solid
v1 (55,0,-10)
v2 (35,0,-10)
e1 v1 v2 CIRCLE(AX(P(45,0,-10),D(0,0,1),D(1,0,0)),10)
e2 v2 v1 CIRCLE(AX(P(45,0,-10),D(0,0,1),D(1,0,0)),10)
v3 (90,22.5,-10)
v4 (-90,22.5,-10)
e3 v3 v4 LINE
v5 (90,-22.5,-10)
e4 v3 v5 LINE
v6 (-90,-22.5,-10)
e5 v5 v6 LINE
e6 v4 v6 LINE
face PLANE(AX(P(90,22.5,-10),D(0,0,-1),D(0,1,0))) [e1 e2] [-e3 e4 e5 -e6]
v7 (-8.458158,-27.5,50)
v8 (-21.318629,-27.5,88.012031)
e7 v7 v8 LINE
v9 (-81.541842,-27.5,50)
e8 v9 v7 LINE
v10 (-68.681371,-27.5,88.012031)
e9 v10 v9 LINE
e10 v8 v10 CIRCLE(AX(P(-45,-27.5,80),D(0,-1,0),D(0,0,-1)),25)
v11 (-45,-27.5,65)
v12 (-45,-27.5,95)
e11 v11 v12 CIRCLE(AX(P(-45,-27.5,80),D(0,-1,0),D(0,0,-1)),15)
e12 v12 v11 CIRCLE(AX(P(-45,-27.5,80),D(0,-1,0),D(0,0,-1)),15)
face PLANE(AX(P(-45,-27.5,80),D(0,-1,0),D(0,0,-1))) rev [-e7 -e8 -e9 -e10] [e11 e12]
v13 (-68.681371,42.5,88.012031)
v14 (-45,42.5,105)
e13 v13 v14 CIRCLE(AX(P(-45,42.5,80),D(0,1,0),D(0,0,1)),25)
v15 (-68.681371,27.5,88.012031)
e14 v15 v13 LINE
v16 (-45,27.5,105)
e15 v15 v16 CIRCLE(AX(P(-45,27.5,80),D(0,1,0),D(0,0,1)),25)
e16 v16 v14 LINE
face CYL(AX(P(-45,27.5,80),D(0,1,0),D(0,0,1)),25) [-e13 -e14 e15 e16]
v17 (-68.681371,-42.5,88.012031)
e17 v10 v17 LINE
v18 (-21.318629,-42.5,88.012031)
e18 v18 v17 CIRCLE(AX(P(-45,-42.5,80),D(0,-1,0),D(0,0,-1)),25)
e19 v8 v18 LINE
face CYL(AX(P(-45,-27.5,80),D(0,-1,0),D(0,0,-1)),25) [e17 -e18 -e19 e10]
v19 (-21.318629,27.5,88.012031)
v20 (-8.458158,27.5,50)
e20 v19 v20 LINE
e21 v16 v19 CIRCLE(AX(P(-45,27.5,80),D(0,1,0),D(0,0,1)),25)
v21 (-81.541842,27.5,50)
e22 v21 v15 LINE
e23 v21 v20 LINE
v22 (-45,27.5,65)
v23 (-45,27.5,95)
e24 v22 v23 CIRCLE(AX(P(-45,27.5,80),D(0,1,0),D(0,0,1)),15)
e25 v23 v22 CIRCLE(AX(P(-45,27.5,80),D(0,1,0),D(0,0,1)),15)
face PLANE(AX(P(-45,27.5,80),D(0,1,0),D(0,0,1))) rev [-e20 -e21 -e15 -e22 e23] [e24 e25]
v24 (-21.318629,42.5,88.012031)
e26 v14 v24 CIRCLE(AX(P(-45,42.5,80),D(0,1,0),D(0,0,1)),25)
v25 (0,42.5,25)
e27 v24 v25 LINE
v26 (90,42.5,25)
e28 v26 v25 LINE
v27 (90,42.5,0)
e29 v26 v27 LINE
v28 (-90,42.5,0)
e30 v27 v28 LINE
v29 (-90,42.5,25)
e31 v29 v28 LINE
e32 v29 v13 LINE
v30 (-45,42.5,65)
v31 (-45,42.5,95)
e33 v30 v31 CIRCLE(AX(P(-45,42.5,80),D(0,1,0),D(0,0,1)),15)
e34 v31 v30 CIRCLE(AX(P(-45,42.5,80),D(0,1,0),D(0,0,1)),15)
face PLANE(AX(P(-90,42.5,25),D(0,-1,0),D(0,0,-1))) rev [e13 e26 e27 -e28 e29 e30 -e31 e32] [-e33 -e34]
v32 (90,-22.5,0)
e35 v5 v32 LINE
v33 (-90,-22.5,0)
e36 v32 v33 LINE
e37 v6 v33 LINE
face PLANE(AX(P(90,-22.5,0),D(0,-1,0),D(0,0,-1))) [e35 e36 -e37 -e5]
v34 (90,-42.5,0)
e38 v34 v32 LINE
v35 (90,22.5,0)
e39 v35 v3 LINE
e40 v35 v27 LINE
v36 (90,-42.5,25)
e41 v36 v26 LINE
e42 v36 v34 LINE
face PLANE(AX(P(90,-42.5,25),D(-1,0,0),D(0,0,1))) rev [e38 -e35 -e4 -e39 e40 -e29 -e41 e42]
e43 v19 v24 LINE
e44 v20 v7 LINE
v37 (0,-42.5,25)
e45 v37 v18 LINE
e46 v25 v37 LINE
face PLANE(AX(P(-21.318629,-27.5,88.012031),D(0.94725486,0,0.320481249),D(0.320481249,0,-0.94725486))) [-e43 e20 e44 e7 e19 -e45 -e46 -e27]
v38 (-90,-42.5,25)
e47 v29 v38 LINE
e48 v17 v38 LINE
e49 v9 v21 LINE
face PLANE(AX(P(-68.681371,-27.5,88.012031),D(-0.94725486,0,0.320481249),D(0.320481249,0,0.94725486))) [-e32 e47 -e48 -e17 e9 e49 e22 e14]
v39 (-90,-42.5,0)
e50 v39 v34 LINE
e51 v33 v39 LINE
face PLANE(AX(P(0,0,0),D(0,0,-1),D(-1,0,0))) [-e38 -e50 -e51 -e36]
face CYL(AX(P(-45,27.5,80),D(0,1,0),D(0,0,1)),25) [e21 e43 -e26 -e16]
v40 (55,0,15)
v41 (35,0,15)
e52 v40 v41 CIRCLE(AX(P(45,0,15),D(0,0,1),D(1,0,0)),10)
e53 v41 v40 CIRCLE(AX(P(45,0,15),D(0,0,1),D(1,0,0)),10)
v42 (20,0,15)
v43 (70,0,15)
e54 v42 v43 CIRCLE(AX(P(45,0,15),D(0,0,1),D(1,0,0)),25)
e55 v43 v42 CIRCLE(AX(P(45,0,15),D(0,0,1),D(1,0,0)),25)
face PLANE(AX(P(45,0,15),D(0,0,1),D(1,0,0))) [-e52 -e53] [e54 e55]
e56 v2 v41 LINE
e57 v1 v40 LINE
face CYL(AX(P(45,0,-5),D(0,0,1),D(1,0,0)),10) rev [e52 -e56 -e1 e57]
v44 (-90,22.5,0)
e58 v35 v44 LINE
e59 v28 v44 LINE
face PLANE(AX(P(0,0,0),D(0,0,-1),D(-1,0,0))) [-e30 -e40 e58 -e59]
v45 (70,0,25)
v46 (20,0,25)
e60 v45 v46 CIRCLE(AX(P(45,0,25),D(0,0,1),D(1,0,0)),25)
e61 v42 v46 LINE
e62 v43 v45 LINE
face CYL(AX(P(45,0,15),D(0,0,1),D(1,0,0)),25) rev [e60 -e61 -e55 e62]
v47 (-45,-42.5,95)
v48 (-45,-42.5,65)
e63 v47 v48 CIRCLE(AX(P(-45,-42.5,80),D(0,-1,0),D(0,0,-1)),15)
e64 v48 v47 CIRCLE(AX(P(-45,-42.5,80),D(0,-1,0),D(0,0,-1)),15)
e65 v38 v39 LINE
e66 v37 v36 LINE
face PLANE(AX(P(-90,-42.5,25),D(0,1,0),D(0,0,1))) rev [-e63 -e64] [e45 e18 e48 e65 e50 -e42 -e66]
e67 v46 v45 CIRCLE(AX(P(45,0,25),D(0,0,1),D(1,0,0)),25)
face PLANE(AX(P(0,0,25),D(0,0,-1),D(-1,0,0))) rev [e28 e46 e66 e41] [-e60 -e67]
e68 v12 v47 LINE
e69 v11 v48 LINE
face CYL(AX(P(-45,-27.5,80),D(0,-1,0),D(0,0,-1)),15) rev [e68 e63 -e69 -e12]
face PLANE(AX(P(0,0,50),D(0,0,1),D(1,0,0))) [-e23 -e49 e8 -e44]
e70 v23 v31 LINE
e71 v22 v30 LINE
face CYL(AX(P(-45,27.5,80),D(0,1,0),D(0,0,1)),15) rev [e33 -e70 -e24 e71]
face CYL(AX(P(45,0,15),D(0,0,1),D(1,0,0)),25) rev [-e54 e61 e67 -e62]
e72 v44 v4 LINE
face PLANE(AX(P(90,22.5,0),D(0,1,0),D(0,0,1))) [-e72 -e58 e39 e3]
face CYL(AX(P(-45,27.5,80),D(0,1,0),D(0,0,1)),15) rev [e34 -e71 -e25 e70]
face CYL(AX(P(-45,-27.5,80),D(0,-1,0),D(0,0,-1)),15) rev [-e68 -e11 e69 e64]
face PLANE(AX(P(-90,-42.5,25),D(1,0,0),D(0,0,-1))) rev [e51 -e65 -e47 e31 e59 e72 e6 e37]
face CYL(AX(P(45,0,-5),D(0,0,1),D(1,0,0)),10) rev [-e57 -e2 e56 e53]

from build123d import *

# Parameters (mm, degrees)
BASE_PLATE_SKETCH_W   = 180
BASE_PLATE_SKETCH_H   = 85
BASE_PLATE_DEPTH      = 25
COUNTERBORE_SKETCH_R  = 25
COUNTERBORE_50_DEPTH  = 10
THROUGH_HOLE_SKETCH_R = 10
THROUGH_HOLE_20_DEPTH = 20
BACK_KEY_SKETCH_W     = 10
BACK_KEY_SKETCH_H     = 45
BACK_KEY_DEPTH        = 180
KEY_RELIEF_SKETCH_R   = 10
KEY_RELIEF_CUT_DEPTH  = 103.621878759
UPPER_LUG_SKETCH_R    = 15
UPPER_LUG_DEPTH       = 15
LOWER_START           = -15
LOWER_LUG_SKETCH_R    = 15
LOWER_LUG_DEPTH       = 15
LUG_WEB_SKETCH_W      = 90
LUG_WEB_SKETCH_H      = 55
LUG_WEB_DEPTH         = 25
WEB_CUT_A_DEPTH       = 156
WEB_CUT_B_DEPTH       = 156


with BuildPart() as part:
    # Base Plate Sketch → Base Plate (new body)
    with BuildSketch(Plane.XY):
        Rectangle(BASE_PLATE_SKETCH_W, BASE_PLATE_SKETCH_H)
    extrude(amount=BASE_PLATE_DEPTH)

    # Counterbore Sketch → Counterbore Ø50 (cut)
    with BuildSketch(Plane.XY.offset(25)):
        with Locations((45, 0)):
            Circle(COUNTERBORE_SKETCH_R)
    extrude(amount=-COUNTERBORE_50_DEPTH, mode=Mode.SUBTRACT)

    # Through Hole Sketch → Through Hole Ø20 (cut)
    with BuildSketch(Plane.XY.offset(15)):
        with Locations((45, 0)):
            Circle(THROUGH_HOLE_SKETCH_R)
    extrude(amount=-THROUGH_HOLE_20_DEPTH, mode=Mode.SUBTRACT)

    # Back Key Sketch → Back Key (add, through all)
    with BuildSketch(Plane.ZY.offset(90)):
        with Locations((-5, 0)):
            Rectangle(BACK_KEY_SKETCH_W, BACK_KEY_SKETCH_H)
    extrude(amount=-BACK_KEY_DEPTH)

    # Key Relief Sketch → Key Relief Cut (cut, through all)
    with BuildSketch(Plane.XY):
        with Locations((45, 0)):
            Circle(KEY_RELIEF_SKETCH_R)
    extrude(amount=-KEY_RELIEF_CUT_DEPTH, mode=Mode.SUBTRACT)

    # Upper Lug Sketch → Upper Lug (add)
    with BuildSketch(Plane.XZ.offset(42.5)):
        with BuildLine():
            Line((-68.681371492, 88.01203122), (-90, 25))
            Line((-90, 25), (0, 25))
            Line((0, 25), (-21.318628508, 88.01203122))
            ThreePointArc((-21.318628508, 88.01203122), (-45, 105), (-68.681371492, 88.01203122))
        make_face()
        with Locations(Location((-45, 80, 0), (0, 0, 270))):
            Circle(UPPER_LUG_SKETCH_R, mode=Mode.SUBTRACT)
    extrude(amount=-UPPER_LUG_DEPTH)

    # Lower Lug Sketch → Lower Lug (add)
    with BuildSketch(Plane(origin=(0, 42.5, 0), x_dir=(1, 0, 0), z_dir=(0, 1, 0)).offset(LOWER_START)):
        with BuildLine():
            Line((-90, -25), (-68.681371492, -88.01203122))
            ThreePointArc((-68.681371492, -88.01203122), (-45, -105), (-21.318628508, -88.01203122))
            Line((-21.318628508, -88.01203122), (0, -25))
            Line((0, -25), (-90, -25))
        make_face()
        with Locations(Location((-45, -80, 0), (0, 0, 90))):
            Circle(LOWER_LUG_SKETCH_R, mode=Mode.SUBTRACT)
    extrude(amount=LOWER_LUG_DEPTH)

    # Lug Web Sketch → Lug Web (add)
    with BuildSketch(Plane.XY.offset(25)):
        with Locations((-45, 0)):
            Rectangle(LUG_WEB_SKETCH_W, LUG_WEB_SKETCH_H)
    extrude(amount=LUG_WEB_DEPTH)

    # Web Cut A Sketch → Web Cut A (cut, through all)
    with BuildSketch(Plane(origin=(0, 27.5, 0), x_dir=(1, 0, 0), z_dir=(0, 1, 0))):
        Polygon((0, -25), (-8.458157948, -50), (0, -50), align=None)
    extrude(amount=-WEB_CUT_A_DEPTH, mode=Mode.SUBTRACT)

    # Web Cut B Sketch → Web Cut B (cut, through all)
    with BuildSketch(Plane.XZ.offset(27.5)):
        Polygon((-90, 25), (-81.541842052, 50), (-90, 50), align=None)
    extrude(amount=-WEB_CUT_B_DEPTH, mode=Mode.SUBTRACT)


solid = part.part
